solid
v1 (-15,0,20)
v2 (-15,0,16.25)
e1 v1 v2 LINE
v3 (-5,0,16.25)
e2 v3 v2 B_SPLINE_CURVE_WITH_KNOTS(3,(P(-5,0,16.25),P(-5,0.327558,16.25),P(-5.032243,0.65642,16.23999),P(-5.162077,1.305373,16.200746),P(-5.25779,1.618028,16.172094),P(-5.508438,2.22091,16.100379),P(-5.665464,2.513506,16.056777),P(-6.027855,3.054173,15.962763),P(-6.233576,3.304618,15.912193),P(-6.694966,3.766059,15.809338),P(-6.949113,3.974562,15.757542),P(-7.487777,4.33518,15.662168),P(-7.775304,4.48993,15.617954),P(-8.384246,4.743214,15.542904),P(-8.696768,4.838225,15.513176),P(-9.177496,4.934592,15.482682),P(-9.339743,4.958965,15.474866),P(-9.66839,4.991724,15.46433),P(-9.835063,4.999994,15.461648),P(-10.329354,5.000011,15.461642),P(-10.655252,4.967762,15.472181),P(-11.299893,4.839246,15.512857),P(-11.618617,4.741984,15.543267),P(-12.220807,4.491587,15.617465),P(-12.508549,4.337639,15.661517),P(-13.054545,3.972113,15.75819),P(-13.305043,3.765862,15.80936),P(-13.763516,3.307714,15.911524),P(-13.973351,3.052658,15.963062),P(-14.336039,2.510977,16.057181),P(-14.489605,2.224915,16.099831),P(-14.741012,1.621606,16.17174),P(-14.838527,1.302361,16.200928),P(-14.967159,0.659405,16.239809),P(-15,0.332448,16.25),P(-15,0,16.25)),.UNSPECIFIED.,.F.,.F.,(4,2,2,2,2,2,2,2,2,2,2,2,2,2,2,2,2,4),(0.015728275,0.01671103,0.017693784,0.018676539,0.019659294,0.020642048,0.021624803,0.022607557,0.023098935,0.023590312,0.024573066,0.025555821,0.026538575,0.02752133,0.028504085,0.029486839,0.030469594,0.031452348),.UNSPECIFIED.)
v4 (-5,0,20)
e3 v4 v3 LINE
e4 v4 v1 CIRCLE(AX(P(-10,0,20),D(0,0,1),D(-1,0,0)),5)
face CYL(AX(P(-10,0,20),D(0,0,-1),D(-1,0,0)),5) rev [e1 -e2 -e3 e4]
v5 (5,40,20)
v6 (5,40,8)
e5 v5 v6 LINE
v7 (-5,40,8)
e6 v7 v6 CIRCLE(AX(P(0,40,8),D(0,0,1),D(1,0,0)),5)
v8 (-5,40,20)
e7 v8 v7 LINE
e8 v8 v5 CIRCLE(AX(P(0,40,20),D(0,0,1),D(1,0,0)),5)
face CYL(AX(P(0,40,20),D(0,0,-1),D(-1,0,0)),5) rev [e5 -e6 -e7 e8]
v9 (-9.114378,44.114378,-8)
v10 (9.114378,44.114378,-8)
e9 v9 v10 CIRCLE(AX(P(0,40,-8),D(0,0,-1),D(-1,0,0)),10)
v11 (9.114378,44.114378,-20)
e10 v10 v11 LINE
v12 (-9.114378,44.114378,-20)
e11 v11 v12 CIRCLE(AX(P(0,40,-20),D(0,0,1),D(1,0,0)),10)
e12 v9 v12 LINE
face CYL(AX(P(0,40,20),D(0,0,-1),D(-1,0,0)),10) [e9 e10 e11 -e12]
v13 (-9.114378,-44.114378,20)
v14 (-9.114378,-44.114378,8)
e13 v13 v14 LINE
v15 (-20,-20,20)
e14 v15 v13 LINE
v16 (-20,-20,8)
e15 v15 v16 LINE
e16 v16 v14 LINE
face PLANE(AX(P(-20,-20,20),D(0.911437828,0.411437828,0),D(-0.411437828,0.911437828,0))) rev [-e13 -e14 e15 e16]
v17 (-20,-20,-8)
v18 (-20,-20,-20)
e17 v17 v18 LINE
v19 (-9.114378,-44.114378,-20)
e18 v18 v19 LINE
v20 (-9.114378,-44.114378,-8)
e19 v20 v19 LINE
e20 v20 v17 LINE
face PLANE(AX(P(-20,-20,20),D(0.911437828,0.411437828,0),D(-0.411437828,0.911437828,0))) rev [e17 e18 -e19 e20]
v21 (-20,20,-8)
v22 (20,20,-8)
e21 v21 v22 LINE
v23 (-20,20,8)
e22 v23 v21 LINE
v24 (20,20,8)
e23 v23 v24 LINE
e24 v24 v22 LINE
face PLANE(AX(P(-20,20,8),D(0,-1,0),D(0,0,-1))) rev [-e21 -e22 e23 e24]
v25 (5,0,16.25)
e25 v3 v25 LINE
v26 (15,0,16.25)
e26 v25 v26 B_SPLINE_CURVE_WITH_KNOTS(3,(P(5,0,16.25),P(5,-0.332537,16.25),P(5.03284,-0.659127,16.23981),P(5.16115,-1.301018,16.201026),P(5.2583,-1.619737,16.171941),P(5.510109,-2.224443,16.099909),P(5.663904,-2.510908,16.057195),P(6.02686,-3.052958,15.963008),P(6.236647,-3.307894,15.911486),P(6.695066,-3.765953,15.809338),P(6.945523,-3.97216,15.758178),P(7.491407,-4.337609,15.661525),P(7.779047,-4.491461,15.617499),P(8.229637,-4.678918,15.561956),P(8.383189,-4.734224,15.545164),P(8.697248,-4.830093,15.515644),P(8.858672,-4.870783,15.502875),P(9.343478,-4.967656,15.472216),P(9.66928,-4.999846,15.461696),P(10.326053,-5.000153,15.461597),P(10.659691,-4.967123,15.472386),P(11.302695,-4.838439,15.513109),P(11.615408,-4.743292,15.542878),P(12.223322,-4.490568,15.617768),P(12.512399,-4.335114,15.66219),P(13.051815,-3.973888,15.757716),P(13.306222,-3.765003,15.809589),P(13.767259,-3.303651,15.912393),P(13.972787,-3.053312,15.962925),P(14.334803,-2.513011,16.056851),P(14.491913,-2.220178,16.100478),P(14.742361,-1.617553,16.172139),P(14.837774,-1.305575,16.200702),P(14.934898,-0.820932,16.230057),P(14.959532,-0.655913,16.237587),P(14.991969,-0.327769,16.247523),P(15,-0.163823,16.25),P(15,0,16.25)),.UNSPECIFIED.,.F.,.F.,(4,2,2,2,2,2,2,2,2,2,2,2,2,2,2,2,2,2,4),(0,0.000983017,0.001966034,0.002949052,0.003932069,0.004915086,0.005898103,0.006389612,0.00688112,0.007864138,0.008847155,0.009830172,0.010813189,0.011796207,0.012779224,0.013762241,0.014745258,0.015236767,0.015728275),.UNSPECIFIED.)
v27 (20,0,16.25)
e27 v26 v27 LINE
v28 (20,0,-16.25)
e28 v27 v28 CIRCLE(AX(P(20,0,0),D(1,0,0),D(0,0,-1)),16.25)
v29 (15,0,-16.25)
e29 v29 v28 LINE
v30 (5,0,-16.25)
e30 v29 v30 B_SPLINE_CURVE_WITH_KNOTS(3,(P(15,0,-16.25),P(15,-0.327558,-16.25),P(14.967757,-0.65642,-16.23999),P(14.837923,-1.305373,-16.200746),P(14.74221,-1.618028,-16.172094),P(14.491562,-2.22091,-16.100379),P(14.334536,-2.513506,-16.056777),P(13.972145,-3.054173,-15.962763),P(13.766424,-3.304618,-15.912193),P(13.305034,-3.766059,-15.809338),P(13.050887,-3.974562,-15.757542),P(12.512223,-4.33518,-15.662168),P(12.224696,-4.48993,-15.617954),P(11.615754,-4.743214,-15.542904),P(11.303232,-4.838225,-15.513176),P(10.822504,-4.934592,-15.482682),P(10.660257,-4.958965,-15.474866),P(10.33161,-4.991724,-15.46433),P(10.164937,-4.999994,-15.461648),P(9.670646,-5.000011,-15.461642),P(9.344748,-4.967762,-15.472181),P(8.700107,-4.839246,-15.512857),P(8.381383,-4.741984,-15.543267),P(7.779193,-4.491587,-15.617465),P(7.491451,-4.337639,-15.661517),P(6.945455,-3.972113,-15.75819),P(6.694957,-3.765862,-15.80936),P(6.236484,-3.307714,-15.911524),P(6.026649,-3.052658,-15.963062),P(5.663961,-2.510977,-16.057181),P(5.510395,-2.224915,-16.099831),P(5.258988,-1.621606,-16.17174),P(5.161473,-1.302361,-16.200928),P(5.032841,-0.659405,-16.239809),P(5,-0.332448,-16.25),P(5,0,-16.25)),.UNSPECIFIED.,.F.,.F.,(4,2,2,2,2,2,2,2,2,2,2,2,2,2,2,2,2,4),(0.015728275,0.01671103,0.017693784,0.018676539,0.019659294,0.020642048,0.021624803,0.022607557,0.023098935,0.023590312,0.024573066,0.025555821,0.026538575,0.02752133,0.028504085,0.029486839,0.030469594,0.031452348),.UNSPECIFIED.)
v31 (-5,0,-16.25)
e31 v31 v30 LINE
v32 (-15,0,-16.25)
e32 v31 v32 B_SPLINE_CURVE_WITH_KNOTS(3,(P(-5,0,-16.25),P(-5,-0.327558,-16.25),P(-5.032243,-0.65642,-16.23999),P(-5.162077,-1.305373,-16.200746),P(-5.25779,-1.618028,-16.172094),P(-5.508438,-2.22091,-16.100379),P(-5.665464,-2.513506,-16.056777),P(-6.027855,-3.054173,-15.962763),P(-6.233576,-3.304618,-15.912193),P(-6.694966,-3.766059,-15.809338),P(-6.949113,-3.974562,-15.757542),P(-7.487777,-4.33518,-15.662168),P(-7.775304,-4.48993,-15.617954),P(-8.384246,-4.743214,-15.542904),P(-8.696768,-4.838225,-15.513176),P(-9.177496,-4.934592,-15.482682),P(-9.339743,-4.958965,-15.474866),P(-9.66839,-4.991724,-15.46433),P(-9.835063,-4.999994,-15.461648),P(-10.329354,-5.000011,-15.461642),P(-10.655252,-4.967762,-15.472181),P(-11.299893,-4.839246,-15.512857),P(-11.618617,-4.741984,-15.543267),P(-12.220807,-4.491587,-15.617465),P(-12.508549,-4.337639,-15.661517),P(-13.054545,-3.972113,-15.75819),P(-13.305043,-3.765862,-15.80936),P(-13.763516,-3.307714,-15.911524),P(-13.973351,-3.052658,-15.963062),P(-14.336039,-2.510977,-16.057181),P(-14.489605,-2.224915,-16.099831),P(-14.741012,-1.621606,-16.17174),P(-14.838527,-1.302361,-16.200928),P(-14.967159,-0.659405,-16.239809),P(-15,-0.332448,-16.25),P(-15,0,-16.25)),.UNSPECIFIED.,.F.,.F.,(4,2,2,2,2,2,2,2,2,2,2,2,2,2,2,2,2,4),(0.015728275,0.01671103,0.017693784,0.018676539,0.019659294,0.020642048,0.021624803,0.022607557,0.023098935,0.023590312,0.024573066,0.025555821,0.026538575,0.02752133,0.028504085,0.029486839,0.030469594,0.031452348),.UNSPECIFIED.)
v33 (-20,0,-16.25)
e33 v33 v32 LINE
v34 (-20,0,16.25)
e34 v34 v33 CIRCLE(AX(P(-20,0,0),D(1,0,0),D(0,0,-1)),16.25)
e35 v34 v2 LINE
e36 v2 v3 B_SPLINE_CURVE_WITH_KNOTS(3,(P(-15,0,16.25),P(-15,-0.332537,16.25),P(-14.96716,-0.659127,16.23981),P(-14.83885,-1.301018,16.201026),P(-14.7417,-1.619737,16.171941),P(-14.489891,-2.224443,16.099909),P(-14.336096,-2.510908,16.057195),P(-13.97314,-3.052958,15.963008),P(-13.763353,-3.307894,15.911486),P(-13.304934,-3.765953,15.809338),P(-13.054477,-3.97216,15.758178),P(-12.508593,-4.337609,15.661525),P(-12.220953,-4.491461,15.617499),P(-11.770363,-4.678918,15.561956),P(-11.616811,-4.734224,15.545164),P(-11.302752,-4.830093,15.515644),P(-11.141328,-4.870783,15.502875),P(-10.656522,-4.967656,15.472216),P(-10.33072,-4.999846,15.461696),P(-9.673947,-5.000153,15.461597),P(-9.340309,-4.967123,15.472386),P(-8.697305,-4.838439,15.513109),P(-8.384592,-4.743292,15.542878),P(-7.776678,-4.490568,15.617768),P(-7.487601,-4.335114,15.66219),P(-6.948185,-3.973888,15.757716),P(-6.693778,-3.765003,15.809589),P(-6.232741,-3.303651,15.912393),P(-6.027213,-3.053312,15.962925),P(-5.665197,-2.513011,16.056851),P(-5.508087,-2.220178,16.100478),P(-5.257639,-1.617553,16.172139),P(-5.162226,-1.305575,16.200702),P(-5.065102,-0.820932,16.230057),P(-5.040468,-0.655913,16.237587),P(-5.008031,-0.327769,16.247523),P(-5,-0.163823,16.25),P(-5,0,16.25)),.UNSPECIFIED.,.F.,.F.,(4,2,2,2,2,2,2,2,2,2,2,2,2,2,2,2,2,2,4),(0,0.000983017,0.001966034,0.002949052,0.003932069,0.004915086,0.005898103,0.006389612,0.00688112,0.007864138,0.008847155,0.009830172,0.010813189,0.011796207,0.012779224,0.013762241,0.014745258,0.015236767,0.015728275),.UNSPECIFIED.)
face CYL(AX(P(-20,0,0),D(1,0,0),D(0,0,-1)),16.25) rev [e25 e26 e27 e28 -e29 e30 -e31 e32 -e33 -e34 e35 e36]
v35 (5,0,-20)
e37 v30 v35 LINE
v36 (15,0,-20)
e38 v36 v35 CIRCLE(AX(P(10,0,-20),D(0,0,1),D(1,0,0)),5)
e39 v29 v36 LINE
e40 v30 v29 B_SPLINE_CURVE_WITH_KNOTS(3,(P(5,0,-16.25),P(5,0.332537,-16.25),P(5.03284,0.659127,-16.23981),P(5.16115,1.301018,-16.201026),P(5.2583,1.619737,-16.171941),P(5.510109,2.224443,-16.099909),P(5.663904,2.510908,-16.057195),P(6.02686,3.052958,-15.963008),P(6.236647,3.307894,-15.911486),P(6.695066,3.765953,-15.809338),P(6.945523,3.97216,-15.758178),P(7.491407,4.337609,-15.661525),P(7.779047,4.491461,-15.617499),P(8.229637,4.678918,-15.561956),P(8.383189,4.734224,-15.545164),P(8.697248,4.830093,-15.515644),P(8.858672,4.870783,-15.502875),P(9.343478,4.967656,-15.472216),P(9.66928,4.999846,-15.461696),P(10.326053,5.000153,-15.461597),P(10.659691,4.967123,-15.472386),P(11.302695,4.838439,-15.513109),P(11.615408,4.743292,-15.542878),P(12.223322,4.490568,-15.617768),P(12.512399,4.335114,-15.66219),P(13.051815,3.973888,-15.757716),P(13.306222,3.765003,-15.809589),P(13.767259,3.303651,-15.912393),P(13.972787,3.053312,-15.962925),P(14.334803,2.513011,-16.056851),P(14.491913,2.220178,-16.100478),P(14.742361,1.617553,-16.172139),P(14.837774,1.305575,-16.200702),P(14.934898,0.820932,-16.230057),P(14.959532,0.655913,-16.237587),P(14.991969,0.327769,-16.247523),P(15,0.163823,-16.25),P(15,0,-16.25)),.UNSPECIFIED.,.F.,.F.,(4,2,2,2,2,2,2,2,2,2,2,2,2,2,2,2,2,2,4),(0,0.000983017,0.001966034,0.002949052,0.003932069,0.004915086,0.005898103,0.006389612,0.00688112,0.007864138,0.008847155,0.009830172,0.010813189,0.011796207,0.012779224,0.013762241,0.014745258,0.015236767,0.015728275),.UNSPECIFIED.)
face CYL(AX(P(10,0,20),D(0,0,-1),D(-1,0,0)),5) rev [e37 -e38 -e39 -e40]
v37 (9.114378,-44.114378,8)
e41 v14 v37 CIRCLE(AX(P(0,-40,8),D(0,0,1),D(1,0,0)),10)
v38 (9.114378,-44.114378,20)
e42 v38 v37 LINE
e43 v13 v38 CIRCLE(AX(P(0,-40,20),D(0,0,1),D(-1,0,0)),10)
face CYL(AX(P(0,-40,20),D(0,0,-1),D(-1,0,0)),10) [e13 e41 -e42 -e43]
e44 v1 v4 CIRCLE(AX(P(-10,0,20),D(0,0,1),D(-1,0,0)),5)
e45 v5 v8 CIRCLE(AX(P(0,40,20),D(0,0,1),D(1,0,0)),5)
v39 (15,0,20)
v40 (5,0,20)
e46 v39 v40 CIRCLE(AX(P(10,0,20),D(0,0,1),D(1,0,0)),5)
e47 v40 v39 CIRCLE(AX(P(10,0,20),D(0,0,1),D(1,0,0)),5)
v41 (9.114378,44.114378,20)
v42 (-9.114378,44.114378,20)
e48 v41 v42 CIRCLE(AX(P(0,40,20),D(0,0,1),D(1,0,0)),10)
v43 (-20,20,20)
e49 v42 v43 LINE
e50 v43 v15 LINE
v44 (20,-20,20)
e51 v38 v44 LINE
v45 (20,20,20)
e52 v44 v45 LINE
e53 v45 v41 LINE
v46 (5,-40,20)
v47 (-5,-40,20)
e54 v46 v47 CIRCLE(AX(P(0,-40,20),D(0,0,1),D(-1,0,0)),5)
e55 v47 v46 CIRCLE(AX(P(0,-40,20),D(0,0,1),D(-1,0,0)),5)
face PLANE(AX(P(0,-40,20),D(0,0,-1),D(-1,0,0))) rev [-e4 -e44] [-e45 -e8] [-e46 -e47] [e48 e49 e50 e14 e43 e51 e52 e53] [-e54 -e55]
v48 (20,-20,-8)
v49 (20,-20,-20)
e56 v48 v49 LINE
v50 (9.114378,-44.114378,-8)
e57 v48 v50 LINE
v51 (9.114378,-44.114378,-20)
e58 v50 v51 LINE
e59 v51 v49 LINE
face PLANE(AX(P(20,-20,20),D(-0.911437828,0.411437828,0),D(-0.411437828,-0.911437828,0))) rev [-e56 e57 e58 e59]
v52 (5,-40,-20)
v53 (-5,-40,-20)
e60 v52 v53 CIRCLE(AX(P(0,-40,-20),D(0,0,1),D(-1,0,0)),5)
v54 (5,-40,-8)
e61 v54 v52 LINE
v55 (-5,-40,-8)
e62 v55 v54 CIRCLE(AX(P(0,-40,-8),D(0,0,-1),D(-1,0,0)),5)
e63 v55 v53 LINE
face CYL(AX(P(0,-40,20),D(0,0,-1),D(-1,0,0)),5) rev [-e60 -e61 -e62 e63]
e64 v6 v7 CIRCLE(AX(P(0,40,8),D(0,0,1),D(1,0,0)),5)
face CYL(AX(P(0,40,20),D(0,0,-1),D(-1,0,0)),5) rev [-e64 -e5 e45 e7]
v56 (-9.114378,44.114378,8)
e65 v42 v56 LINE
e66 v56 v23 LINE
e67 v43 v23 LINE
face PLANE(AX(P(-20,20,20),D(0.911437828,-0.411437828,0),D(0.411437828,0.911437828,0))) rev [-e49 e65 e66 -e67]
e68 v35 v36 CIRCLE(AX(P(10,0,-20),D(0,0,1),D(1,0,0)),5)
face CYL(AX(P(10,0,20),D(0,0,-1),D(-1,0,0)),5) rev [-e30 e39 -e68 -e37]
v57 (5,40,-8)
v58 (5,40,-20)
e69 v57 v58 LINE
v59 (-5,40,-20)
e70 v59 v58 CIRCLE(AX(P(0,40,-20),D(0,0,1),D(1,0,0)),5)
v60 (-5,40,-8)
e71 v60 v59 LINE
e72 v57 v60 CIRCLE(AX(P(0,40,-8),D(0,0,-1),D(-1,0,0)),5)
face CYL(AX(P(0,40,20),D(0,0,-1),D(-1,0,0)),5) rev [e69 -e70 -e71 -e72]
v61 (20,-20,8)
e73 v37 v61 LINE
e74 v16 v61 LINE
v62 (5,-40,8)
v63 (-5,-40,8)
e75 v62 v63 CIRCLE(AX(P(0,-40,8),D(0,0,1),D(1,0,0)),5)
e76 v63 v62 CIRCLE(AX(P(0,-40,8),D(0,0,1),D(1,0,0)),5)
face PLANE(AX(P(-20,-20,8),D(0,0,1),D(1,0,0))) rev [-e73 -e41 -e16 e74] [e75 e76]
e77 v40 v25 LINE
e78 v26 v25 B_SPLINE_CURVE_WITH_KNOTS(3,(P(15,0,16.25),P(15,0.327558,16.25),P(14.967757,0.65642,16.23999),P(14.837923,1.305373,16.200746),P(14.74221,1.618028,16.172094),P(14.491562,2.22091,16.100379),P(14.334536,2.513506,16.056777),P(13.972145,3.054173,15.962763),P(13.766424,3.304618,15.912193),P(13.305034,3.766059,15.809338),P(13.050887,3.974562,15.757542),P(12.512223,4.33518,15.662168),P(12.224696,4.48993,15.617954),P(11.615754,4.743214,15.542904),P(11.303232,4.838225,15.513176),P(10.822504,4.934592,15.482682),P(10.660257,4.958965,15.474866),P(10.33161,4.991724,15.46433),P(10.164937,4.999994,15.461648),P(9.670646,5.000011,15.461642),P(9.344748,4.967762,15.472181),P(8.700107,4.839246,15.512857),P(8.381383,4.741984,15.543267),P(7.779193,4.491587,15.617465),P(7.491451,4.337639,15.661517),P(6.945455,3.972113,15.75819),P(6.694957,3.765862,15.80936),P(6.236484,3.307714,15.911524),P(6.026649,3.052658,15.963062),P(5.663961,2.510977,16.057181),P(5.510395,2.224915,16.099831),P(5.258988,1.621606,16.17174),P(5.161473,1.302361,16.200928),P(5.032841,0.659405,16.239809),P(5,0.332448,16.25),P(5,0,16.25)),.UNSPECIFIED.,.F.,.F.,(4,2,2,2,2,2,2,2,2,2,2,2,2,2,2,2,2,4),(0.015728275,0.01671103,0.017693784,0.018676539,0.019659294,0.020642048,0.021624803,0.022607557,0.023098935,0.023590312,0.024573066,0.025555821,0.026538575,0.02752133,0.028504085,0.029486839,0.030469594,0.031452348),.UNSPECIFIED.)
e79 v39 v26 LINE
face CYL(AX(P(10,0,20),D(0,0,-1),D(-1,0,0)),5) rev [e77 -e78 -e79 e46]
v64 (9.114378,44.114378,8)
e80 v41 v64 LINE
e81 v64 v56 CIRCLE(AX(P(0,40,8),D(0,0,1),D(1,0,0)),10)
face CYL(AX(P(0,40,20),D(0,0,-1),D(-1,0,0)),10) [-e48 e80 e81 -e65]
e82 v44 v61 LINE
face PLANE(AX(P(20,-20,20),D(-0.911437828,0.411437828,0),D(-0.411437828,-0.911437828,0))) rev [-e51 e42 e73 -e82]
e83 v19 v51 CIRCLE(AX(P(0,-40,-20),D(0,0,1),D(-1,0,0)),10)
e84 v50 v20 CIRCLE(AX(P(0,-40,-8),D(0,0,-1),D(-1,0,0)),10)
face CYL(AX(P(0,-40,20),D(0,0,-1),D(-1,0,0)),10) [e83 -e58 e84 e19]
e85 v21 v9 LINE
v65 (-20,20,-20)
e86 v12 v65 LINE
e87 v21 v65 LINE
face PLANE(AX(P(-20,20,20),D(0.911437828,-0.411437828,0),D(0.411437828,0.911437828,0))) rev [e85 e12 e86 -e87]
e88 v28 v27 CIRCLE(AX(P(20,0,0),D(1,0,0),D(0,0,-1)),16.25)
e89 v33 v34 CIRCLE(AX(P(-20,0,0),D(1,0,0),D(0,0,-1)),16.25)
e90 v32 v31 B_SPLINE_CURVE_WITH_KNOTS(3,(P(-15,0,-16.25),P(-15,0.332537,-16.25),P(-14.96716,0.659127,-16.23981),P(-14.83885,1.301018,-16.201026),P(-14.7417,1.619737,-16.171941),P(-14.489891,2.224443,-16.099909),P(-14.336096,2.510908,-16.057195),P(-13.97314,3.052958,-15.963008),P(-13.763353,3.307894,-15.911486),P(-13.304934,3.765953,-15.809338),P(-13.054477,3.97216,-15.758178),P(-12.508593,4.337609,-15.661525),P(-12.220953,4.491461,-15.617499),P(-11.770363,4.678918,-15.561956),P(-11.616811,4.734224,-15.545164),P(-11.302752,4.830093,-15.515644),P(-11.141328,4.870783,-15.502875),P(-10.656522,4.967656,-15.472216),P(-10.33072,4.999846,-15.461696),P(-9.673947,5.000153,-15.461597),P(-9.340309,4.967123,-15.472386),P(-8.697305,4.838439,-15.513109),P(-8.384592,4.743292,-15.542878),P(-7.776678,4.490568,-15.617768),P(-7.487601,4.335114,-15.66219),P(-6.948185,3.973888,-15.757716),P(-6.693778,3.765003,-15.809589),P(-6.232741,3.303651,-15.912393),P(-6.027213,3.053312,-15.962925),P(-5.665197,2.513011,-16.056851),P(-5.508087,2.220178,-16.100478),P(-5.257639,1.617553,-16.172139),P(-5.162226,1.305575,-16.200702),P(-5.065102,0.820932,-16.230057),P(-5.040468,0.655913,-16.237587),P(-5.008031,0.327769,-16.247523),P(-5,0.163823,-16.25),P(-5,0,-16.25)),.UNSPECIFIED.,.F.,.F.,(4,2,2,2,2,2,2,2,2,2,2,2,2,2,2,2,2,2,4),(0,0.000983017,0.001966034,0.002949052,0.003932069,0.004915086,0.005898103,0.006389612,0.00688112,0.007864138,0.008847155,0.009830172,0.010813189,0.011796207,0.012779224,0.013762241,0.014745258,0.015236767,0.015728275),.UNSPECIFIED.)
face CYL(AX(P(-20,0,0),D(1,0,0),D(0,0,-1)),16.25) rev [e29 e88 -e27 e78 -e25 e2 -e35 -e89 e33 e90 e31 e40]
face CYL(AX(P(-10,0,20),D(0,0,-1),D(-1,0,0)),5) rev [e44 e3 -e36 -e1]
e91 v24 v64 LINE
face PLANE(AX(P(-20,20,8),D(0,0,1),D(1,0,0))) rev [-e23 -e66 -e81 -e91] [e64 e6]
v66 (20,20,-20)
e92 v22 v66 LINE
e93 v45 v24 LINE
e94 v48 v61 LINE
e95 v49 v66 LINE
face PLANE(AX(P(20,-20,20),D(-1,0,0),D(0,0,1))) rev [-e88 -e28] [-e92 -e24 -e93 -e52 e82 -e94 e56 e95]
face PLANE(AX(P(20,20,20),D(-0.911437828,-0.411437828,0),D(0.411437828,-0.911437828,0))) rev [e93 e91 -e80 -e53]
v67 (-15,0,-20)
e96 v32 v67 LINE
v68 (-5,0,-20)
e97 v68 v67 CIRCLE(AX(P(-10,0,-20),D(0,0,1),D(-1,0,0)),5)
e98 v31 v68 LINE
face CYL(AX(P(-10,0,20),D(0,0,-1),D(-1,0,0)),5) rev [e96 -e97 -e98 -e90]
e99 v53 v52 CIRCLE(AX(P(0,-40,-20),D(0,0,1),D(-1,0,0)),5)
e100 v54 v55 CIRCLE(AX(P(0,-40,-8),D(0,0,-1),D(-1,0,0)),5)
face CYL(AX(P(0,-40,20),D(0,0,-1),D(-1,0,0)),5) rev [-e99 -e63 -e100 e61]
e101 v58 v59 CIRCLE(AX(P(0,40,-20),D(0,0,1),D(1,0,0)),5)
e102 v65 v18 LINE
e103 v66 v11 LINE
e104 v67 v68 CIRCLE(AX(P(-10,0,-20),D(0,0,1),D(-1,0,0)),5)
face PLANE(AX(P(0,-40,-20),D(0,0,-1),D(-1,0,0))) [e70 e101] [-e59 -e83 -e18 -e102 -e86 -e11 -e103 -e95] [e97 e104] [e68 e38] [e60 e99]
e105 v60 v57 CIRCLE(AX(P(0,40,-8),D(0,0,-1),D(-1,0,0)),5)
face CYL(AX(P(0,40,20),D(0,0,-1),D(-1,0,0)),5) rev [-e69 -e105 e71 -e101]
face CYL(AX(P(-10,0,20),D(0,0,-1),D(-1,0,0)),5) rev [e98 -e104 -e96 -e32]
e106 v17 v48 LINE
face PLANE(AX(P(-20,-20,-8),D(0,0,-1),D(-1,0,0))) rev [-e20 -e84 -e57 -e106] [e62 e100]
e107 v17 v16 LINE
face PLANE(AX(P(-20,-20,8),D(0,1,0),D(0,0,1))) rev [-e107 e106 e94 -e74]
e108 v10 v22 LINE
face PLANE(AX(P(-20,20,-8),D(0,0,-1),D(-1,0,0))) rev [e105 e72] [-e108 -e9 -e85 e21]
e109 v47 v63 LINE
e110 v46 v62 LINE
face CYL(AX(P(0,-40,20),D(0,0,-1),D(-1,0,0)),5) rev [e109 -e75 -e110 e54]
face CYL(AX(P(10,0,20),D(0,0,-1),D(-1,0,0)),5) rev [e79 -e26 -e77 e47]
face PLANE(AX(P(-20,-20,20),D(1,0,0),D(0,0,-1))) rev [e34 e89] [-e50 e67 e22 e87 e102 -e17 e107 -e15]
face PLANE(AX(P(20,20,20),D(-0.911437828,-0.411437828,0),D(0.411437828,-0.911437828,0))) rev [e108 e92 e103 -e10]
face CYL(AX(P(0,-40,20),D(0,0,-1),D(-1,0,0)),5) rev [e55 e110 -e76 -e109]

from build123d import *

# Parameters (mm, degrees)
SKETCH_1_R               = 5
EXTRUDE_1_DEPTH          = 20
CUT_EXTRUDE_1_DEPTH      = 58.445626465
CUT_EXTRUDE_1_DEPTH_BACK = 58.445626465
SKETCH_2_R               = 16.25
SKETCH_2_W               = 16
SKETCH_2_H               = 60


with BuildPart() as part:
    # 草图1 → 凸台-拉伸1 (new, symmetric)
    with BuildSketch(Plane.XY):
        with BuildLine():
            Line((20, -20), (20, 20))
            Line((20, 20), (9.114378278, 44.114378278))
            ThreePointArc((9.114378278, 44.114378278), (0, 50), (-9.114378278, 44.114378278))
            Line((-9.114378278, 44.114378278), (-20, 20))
            Line((-20, 20), (-20, -20))
            Line((-20, -20), (-9.114378278, -44.114378278))
            ThreePointArc((-9.114378278, -44.114378278), (0, -50), (9.114378278, -44.114378278))
            Line((9.114378278, -44.114378278), (20, -20))
        make_face()
        with Locations((0, 40)):
            Circle(SKETCH_1_R, mode=Mode.SUBTRACT)
        with Locations((10, 0)):
            Circle(SKETCH_1_R, mode=Mode.SUBTRACT)
        with Locations(Location((0, -40, 0), (0, 0, 180))):
            Circle(SKETCH_1_R, mode=Mode.SUBTRACT)
        with Locations(Location((-10, 0, 0), (0, 0, 180))):
            Circle(SKETCH_1_R, mode=Mode.SUBTRACT)
    extrude(amount=EXTRUDE_1_DEPTH, both=True)

    # 草图2 → 切除-拉伸1 (cut, two sides: drawn at the far end of the back side and taken through both)
    with BuildSketch(Plane(origin=(0, 0, 0), x_dir=(0, 0, -1), z_dir=(1, 0, 0)).offset(-CUT_EXTRUDE_1_DEPTH_BACK)):
        Circle(SKETCH_2_R)
        with Locations((0, 50)):
            Rectangle(SKETCH_2_W, SKETCH_2_H)
        with Locations((0, -50)):
            Rectangle(SKETCH_2_W, SKETCH_2_H)
    extrude(amount=CUT_EXTRUDE_1_DEPTH + CUT_EXTRUDE_1_DEPTH_BACK, mode=Mode.SUBTRACT)


solid = part.part
